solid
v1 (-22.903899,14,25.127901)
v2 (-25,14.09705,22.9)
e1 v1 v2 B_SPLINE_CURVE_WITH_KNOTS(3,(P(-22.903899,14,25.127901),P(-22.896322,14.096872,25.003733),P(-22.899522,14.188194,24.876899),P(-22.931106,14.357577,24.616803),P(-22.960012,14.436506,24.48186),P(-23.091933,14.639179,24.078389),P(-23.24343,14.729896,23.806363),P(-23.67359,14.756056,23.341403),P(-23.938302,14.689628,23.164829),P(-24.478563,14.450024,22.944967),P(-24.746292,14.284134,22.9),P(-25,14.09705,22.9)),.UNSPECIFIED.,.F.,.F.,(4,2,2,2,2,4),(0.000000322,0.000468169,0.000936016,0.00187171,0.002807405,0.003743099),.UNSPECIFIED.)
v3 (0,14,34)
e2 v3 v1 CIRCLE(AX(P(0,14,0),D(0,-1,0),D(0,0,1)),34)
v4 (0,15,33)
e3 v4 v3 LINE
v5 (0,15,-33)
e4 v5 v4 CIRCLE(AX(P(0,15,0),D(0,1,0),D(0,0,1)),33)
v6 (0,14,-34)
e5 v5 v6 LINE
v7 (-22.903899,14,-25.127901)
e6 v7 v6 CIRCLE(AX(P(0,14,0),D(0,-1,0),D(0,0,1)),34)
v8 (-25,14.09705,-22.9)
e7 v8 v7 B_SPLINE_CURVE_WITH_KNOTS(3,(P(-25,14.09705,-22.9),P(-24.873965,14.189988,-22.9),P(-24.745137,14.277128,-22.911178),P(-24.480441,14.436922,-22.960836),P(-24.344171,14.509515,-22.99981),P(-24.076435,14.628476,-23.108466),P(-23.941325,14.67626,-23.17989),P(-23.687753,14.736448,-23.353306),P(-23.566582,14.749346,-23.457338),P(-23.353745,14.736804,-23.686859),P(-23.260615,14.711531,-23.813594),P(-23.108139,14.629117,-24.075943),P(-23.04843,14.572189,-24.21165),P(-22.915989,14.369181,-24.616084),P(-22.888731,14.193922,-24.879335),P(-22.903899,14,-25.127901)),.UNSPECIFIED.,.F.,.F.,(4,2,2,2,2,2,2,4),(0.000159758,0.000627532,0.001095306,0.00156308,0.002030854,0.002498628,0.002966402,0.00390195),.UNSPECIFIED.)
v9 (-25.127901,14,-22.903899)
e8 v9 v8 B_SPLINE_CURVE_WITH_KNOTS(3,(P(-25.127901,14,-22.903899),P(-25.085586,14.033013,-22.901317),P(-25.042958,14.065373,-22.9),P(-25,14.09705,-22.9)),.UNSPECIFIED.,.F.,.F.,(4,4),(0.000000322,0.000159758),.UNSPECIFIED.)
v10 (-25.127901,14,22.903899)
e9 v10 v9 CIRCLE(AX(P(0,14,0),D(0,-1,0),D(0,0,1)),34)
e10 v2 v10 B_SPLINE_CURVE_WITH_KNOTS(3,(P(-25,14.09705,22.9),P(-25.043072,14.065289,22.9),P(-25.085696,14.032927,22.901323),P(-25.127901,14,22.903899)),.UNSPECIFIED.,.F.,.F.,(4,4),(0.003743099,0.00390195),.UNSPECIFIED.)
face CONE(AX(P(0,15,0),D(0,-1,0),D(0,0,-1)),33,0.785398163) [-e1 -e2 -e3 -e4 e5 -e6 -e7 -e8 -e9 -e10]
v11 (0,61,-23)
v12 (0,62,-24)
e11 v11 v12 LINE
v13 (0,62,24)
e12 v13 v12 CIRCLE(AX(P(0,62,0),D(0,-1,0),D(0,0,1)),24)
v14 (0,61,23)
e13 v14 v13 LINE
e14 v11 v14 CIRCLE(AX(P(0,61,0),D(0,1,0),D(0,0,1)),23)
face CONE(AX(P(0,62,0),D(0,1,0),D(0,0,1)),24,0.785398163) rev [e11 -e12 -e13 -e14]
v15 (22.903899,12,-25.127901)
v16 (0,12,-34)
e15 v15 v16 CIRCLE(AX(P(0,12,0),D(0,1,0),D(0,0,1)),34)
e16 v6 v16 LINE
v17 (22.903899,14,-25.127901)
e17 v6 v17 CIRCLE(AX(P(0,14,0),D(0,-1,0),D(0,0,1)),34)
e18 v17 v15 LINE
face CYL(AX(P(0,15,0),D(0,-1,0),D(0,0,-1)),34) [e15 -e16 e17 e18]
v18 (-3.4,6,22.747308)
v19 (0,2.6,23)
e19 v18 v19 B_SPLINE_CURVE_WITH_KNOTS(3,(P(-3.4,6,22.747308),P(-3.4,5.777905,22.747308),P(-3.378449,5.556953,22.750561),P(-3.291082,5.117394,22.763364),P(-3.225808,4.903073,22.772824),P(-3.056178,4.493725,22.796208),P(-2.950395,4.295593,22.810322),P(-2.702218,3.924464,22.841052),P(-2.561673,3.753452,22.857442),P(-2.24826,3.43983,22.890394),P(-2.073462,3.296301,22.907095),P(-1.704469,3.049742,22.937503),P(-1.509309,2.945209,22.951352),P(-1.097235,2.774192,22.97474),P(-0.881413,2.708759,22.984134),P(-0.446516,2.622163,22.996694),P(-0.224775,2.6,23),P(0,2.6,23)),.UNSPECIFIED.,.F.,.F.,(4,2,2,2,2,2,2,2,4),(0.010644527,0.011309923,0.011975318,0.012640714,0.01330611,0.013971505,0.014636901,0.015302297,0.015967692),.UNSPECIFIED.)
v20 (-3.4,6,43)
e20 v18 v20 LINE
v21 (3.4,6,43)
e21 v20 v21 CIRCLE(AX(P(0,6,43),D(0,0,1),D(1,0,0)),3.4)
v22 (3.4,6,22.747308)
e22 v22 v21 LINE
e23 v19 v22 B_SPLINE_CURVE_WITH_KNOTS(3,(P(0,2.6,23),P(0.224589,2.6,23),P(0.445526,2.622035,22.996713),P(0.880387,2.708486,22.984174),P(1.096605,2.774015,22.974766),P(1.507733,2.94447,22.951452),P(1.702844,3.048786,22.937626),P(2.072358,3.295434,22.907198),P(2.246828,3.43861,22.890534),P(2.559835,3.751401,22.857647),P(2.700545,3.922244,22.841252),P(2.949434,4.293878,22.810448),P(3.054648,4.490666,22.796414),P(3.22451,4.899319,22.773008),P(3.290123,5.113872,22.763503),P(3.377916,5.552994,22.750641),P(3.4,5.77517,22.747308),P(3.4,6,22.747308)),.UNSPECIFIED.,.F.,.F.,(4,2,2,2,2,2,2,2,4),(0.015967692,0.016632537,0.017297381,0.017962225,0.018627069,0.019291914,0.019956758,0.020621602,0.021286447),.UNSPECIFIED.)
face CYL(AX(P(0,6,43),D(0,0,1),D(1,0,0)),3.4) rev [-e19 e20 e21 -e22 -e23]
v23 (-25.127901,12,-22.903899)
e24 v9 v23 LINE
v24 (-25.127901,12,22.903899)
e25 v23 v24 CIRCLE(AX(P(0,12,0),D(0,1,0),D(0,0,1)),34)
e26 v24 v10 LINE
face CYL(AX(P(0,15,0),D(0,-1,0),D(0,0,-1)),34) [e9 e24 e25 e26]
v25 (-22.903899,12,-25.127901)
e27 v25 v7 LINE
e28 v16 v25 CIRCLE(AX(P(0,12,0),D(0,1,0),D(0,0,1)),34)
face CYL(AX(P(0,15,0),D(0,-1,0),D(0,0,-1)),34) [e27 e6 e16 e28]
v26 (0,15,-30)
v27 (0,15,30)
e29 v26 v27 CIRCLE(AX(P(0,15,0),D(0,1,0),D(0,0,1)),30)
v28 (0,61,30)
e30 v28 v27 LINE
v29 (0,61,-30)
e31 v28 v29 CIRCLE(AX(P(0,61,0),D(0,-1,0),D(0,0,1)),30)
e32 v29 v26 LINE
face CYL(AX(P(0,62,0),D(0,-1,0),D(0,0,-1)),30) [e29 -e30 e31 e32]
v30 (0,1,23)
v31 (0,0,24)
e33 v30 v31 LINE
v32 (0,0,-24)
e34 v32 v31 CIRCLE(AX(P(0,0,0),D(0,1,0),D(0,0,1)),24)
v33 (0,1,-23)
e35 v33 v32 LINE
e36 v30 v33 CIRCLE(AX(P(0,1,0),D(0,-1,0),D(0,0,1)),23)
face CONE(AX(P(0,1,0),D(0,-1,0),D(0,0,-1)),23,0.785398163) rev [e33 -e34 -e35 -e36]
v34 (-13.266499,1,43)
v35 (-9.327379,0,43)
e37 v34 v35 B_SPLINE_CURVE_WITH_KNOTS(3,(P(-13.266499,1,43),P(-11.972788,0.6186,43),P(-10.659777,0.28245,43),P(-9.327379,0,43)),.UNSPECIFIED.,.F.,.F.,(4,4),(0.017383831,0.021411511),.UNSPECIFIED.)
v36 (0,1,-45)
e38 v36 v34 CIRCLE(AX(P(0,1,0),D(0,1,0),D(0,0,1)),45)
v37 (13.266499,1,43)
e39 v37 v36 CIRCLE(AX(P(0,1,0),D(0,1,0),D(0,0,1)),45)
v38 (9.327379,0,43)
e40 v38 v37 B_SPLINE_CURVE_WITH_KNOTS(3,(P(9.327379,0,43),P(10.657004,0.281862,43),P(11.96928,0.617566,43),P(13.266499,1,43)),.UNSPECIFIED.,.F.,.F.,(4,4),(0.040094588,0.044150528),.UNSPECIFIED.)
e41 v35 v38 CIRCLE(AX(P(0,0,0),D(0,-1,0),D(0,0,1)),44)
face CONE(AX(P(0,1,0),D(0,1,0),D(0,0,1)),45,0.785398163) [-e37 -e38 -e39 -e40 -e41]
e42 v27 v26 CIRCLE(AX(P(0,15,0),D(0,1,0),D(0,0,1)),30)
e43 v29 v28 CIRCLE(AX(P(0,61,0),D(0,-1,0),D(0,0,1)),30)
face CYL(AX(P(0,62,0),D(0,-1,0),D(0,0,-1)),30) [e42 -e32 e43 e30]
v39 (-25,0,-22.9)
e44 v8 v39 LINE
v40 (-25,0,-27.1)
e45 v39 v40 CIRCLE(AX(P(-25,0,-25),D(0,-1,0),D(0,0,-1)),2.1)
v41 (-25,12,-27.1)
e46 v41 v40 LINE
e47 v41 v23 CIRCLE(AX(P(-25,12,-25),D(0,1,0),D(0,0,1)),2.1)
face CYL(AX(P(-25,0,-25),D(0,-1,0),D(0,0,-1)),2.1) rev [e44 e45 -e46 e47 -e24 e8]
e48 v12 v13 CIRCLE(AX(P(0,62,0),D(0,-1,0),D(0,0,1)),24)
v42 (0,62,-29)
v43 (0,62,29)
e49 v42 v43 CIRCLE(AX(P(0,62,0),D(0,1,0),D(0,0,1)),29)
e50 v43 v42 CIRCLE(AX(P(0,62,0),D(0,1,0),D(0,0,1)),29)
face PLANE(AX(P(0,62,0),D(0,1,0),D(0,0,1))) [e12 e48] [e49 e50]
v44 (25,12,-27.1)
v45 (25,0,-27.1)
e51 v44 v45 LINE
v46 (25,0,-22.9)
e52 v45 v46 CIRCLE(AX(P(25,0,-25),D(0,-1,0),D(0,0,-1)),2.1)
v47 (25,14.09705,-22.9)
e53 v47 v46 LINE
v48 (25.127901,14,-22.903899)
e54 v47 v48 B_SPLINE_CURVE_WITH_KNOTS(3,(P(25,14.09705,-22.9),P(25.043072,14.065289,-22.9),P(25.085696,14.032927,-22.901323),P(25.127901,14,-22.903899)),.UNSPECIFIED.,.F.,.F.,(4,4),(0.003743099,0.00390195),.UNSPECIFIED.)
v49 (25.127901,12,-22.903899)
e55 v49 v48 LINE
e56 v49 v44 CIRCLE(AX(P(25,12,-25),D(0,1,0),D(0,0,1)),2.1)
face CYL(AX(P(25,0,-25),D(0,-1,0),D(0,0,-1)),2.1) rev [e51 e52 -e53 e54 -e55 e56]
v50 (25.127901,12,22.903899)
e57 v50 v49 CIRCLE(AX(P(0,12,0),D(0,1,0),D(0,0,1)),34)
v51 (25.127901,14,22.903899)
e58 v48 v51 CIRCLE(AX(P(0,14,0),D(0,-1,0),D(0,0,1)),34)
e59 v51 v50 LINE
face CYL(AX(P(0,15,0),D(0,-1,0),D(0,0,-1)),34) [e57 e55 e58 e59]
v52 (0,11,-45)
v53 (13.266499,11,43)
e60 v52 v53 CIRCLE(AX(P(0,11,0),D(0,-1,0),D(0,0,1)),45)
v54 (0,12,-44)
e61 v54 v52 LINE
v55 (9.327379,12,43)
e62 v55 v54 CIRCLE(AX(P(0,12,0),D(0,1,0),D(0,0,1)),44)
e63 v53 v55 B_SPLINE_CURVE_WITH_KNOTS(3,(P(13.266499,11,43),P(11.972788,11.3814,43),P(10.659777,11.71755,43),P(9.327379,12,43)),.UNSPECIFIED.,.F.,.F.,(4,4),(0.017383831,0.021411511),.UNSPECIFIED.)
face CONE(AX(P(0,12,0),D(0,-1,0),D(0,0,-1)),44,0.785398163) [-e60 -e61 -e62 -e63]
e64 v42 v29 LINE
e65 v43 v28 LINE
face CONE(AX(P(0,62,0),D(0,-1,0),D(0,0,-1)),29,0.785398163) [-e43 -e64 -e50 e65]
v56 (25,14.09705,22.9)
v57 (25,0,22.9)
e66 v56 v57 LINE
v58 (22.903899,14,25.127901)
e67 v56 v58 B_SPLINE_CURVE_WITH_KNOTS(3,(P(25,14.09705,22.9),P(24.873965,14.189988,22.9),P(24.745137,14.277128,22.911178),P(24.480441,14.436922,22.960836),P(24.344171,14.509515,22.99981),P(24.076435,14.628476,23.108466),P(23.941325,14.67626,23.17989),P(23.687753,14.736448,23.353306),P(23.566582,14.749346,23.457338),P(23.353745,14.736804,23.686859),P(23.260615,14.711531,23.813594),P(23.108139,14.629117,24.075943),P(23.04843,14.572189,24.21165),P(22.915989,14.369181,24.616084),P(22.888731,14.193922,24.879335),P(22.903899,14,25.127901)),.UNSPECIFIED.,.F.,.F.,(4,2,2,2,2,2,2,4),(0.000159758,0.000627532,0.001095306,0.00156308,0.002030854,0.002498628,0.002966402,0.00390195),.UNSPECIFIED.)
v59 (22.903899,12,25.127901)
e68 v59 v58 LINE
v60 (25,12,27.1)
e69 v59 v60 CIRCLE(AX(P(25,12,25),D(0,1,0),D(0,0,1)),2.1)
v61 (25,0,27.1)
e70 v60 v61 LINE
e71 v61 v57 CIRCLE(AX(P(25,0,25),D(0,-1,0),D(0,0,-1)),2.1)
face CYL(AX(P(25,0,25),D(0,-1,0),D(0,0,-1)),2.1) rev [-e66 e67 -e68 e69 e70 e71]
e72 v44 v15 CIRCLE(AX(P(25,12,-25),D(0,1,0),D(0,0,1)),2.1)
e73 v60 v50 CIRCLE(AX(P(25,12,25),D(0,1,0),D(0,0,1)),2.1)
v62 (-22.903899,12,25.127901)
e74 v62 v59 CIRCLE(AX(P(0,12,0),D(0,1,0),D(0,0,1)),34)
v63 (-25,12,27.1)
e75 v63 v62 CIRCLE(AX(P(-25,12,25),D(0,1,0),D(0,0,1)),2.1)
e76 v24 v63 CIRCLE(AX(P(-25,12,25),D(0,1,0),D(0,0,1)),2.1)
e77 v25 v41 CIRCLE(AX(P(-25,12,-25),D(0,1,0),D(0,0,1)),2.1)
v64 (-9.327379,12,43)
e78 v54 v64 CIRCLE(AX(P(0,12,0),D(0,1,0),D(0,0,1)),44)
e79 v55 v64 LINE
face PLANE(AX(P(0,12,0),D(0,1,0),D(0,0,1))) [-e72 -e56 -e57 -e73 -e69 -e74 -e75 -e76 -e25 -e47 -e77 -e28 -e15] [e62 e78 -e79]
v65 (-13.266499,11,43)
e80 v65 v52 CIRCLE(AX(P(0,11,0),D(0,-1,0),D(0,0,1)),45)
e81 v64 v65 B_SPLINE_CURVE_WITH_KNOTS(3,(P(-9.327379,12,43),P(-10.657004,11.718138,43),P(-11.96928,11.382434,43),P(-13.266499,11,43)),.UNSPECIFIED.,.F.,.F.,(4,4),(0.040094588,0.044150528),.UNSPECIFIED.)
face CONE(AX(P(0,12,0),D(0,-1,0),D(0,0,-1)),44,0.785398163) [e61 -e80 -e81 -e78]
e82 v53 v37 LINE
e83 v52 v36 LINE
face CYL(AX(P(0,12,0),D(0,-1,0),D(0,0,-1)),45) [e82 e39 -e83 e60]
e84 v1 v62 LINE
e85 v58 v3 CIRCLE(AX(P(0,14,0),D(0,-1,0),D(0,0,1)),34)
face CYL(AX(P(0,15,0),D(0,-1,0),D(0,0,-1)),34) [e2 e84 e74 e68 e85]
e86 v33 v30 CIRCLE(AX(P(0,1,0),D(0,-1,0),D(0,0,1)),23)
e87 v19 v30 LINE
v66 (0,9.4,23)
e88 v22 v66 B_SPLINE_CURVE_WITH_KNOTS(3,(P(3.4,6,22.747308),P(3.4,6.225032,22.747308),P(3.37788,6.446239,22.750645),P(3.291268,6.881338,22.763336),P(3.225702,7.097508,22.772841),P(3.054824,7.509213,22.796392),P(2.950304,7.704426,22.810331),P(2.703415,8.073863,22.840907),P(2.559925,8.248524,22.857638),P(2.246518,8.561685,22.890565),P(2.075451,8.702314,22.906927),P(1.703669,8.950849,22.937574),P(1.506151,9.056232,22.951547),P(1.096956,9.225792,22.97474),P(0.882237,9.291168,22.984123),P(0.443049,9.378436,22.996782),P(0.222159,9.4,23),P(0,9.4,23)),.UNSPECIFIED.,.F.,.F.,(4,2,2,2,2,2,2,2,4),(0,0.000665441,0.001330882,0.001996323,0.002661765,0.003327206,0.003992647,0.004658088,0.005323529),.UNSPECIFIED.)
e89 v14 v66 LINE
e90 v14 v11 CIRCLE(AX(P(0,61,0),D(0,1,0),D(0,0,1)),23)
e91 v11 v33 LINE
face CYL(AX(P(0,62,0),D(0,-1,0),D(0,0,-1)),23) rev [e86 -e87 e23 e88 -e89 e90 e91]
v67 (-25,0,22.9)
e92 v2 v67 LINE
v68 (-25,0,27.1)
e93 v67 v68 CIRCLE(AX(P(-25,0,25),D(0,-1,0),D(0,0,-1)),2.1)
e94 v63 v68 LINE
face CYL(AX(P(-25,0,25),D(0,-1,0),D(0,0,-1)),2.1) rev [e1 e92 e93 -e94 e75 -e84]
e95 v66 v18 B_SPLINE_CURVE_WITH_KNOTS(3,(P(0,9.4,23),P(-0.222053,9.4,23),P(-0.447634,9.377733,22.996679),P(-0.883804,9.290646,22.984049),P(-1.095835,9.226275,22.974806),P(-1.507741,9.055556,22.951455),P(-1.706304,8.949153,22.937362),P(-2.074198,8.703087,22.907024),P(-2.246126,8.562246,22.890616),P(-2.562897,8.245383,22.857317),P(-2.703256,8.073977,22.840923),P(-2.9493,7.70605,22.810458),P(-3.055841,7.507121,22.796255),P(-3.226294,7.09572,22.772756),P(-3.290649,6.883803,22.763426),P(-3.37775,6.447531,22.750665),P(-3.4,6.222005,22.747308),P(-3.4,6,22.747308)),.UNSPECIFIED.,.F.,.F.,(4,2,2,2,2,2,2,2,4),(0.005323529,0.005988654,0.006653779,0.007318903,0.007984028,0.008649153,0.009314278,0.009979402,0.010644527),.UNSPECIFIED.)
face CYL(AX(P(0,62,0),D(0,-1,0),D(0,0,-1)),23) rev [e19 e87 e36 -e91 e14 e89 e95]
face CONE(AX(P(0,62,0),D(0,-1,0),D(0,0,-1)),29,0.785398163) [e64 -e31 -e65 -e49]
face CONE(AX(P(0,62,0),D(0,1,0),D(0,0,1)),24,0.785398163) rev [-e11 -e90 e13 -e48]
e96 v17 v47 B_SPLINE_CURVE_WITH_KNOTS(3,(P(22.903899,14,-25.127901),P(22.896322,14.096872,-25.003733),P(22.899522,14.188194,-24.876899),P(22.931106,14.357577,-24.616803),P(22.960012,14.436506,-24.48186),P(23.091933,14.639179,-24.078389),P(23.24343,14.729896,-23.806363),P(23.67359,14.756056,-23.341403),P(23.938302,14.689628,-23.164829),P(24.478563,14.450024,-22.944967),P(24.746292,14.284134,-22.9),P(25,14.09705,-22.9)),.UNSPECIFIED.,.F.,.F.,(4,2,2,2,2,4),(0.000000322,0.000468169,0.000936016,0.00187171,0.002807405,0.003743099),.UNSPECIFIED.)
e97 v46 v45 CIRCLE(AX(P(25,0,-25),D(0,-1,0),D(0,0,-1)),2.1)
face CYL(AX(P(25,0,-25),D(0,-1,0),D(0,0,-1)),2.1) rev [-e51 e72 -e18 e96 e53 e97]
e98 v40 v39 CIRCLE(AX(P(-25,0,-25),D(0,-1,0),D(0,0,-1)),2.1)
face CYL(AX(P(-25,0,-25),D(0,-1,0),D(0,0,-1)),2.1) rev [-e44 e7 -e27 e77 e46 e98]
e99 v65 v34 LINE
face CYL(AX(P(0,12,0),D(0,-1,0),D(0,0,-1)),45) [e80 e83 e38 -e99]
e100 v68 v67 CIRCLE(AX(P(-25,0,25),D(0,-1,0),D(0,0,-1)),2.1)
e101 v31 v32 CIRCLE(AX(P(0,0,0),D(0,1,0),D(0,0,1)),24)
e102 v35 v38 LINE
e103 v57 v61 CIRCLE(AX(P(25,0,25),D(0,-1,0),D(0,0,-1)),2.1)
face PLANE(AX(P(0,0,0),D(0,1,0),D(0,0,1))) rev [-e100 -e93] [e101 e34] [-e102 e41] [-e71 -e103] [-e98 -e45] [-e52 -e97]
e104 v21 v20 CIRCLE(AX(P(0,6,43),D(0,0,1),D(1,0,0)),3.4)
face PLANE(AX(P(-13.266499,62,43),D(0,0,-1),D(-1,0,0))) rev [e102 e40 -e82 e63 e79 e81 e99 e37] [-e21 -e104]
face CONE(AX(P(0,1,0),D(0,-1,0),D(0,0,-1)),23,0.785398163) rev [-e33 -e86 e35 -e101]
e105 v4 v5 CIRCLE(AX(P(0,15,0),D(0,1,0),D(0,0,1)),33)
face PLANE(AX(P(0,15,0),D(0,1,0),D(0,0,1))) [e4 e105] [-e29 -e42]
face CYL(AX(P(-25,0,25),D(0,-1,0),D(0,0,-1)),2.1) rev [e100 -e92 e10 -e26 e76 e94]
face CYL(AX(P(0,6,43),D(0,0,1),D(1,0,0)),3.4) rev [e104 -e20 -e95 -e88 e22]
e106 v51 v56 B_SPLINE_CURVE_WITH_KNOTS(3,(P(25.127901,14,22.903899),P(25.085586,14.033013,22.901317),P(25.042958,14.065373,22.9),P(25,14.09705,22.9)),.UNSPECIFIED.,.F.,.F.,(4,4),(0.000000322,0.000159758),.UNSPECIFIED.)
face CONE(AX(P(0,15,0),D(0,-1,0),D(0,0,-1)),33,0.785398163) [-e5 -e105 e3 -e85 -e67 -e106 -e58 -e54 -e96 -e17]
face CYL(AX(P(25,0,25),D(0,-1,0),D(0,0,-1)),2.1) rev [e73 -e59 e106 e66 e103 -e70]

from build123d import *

# Parameters (mm, degrees)
SKETCH_1_R              = 45
EXTRUDE_1_DEPTH         = 12
SKETCH_2_R              = 30
EXTRUDE_2_DEPTH         = 50
SKETCH_11_R             = 34
EXTRUDE_3_DEPTH         = 3
SKETCH_3_R              = 23
CUT_EXTRUDE_1_DEPTH     = 89.848185125
CHAMFER_1_SIZE          = 1
HOLE_WIZARD_M5_1_D      = 4.2
CUT_EXTRUDE_2_DEPTH     = 89.848185125
HOLE_WIZARD_M8_1_REACH  = 118.675
HOLE_WIZARD_M8_1_BORE_R = 3.4


with BuildPart() as part:
    # 草图1 → 凸台-拉伸1 (new body)
    with BuildSketch(Plane(origin=(0, 0, 0), x_dir=(1, 0, 0), z_dir=(0, 1, 0))):
        with Locations(Location((0, 0, 0), (0, 0, 270))):
            Circle(SKETCH_1_R)
    extrude(amount=EXTRUDE_1_DEPTH)

    # 草图2 → 凸台-拉伸2 (add)
    with BuildSketch(Plane(origin=(0, 12, 0), x_dir=(1, 0, 0), z_dir=(0, 1, 0))):
        with Locations(Location((0, 0, 0), (0, 0, 270))):
            Circle(SKETCH_2_R)
    extrude(amount=EXTRUDE_2_DEPTH)

    # 草图11 → 凸台-拉伸3 (add)
    with BuildSketch(Plane(origin=(0, 12, 0), x_dir=(1, 0, 0), z_dir=(0, 1, 0))):
        with Locations(Location((0, 0, 0), (0, 0, 270))):
            Circle(SKETCH_11_R)
    extrude(amount=EXTRUDE_3_DEPTH)

    # 草图3 → 切除-拉伸1 (cut, through all)
    with BuildSketch(Plane.XZ):
        with Locations(Location((0, 0, 0), (0, 0, 270))):
            Circle(SKETCH_3_R)
    extrude(amount=-CUT_EXTRUDE_1_DEPTH, mode=Mode.SUBTRACT)

    # 倒角1
    chamfer_1_edges = [part.edges().sort_by_distance(p)[0] for p in [
        (0, 15, -34),
        (0, 62, 23),
        (0, 0, 23),
        (0, 0, -45),
        (0, 12, -45),
        (0, 62, -30),
    ]]
    chamfer(chamfer_1_edges, length=CHAMFER_1_SIZE)

    # M5 螺纹孔1 (through all)
    with Locations(Plane(origin=(0, 0, 0), x_dir=(-1, 0, 0), z_dir=(0, -1, 0))):
        with Locations((25, -25), (-25, -25), (-25, 25), (25, 25)):
            Hole(HOLE_WIZARD_M5_1_D / 2)

    # 草图8 → 切除-拉伸2 (cut, through all)
    with BuildSketch(Plane.XZ):
        with BuildLine():
            Line((-13.266499161, 43), (13.266499161, 43))
            ThreePointArc((13.266499161, 43), (0, 45), (-13.266499161, 43))
        make_face()
    extrude(amount=-CUT_EXTRUDE_2_DEPTH, mode=Mode.SUBTRACT)

    # M8 螺纹孔1 bore → M8 螺纹孔1 (cut, up to next)
    with BuildSketch(Plane.XY.offset(43), mode=Mode.PRIVATE) as hole_wizard_m8_1_sk1:
        with Locations((0, 6)):
            Circle(HOLE_WIZARD_M8_1_BORE_R)
    hole_wizard_m8_1_tool1 = extrude(hole_wizard_m8_1_sk1.sketch, amount=-HOLE_WIZARD_M8_1_REACH, mode=Mode.PRIVATE) & part.part
    add(hole_wizard_m8_1_tool1.solids().sort_by_distance((0, 6, 43))[0], mode=Mode.SUBTRACT)


solid = part.part
